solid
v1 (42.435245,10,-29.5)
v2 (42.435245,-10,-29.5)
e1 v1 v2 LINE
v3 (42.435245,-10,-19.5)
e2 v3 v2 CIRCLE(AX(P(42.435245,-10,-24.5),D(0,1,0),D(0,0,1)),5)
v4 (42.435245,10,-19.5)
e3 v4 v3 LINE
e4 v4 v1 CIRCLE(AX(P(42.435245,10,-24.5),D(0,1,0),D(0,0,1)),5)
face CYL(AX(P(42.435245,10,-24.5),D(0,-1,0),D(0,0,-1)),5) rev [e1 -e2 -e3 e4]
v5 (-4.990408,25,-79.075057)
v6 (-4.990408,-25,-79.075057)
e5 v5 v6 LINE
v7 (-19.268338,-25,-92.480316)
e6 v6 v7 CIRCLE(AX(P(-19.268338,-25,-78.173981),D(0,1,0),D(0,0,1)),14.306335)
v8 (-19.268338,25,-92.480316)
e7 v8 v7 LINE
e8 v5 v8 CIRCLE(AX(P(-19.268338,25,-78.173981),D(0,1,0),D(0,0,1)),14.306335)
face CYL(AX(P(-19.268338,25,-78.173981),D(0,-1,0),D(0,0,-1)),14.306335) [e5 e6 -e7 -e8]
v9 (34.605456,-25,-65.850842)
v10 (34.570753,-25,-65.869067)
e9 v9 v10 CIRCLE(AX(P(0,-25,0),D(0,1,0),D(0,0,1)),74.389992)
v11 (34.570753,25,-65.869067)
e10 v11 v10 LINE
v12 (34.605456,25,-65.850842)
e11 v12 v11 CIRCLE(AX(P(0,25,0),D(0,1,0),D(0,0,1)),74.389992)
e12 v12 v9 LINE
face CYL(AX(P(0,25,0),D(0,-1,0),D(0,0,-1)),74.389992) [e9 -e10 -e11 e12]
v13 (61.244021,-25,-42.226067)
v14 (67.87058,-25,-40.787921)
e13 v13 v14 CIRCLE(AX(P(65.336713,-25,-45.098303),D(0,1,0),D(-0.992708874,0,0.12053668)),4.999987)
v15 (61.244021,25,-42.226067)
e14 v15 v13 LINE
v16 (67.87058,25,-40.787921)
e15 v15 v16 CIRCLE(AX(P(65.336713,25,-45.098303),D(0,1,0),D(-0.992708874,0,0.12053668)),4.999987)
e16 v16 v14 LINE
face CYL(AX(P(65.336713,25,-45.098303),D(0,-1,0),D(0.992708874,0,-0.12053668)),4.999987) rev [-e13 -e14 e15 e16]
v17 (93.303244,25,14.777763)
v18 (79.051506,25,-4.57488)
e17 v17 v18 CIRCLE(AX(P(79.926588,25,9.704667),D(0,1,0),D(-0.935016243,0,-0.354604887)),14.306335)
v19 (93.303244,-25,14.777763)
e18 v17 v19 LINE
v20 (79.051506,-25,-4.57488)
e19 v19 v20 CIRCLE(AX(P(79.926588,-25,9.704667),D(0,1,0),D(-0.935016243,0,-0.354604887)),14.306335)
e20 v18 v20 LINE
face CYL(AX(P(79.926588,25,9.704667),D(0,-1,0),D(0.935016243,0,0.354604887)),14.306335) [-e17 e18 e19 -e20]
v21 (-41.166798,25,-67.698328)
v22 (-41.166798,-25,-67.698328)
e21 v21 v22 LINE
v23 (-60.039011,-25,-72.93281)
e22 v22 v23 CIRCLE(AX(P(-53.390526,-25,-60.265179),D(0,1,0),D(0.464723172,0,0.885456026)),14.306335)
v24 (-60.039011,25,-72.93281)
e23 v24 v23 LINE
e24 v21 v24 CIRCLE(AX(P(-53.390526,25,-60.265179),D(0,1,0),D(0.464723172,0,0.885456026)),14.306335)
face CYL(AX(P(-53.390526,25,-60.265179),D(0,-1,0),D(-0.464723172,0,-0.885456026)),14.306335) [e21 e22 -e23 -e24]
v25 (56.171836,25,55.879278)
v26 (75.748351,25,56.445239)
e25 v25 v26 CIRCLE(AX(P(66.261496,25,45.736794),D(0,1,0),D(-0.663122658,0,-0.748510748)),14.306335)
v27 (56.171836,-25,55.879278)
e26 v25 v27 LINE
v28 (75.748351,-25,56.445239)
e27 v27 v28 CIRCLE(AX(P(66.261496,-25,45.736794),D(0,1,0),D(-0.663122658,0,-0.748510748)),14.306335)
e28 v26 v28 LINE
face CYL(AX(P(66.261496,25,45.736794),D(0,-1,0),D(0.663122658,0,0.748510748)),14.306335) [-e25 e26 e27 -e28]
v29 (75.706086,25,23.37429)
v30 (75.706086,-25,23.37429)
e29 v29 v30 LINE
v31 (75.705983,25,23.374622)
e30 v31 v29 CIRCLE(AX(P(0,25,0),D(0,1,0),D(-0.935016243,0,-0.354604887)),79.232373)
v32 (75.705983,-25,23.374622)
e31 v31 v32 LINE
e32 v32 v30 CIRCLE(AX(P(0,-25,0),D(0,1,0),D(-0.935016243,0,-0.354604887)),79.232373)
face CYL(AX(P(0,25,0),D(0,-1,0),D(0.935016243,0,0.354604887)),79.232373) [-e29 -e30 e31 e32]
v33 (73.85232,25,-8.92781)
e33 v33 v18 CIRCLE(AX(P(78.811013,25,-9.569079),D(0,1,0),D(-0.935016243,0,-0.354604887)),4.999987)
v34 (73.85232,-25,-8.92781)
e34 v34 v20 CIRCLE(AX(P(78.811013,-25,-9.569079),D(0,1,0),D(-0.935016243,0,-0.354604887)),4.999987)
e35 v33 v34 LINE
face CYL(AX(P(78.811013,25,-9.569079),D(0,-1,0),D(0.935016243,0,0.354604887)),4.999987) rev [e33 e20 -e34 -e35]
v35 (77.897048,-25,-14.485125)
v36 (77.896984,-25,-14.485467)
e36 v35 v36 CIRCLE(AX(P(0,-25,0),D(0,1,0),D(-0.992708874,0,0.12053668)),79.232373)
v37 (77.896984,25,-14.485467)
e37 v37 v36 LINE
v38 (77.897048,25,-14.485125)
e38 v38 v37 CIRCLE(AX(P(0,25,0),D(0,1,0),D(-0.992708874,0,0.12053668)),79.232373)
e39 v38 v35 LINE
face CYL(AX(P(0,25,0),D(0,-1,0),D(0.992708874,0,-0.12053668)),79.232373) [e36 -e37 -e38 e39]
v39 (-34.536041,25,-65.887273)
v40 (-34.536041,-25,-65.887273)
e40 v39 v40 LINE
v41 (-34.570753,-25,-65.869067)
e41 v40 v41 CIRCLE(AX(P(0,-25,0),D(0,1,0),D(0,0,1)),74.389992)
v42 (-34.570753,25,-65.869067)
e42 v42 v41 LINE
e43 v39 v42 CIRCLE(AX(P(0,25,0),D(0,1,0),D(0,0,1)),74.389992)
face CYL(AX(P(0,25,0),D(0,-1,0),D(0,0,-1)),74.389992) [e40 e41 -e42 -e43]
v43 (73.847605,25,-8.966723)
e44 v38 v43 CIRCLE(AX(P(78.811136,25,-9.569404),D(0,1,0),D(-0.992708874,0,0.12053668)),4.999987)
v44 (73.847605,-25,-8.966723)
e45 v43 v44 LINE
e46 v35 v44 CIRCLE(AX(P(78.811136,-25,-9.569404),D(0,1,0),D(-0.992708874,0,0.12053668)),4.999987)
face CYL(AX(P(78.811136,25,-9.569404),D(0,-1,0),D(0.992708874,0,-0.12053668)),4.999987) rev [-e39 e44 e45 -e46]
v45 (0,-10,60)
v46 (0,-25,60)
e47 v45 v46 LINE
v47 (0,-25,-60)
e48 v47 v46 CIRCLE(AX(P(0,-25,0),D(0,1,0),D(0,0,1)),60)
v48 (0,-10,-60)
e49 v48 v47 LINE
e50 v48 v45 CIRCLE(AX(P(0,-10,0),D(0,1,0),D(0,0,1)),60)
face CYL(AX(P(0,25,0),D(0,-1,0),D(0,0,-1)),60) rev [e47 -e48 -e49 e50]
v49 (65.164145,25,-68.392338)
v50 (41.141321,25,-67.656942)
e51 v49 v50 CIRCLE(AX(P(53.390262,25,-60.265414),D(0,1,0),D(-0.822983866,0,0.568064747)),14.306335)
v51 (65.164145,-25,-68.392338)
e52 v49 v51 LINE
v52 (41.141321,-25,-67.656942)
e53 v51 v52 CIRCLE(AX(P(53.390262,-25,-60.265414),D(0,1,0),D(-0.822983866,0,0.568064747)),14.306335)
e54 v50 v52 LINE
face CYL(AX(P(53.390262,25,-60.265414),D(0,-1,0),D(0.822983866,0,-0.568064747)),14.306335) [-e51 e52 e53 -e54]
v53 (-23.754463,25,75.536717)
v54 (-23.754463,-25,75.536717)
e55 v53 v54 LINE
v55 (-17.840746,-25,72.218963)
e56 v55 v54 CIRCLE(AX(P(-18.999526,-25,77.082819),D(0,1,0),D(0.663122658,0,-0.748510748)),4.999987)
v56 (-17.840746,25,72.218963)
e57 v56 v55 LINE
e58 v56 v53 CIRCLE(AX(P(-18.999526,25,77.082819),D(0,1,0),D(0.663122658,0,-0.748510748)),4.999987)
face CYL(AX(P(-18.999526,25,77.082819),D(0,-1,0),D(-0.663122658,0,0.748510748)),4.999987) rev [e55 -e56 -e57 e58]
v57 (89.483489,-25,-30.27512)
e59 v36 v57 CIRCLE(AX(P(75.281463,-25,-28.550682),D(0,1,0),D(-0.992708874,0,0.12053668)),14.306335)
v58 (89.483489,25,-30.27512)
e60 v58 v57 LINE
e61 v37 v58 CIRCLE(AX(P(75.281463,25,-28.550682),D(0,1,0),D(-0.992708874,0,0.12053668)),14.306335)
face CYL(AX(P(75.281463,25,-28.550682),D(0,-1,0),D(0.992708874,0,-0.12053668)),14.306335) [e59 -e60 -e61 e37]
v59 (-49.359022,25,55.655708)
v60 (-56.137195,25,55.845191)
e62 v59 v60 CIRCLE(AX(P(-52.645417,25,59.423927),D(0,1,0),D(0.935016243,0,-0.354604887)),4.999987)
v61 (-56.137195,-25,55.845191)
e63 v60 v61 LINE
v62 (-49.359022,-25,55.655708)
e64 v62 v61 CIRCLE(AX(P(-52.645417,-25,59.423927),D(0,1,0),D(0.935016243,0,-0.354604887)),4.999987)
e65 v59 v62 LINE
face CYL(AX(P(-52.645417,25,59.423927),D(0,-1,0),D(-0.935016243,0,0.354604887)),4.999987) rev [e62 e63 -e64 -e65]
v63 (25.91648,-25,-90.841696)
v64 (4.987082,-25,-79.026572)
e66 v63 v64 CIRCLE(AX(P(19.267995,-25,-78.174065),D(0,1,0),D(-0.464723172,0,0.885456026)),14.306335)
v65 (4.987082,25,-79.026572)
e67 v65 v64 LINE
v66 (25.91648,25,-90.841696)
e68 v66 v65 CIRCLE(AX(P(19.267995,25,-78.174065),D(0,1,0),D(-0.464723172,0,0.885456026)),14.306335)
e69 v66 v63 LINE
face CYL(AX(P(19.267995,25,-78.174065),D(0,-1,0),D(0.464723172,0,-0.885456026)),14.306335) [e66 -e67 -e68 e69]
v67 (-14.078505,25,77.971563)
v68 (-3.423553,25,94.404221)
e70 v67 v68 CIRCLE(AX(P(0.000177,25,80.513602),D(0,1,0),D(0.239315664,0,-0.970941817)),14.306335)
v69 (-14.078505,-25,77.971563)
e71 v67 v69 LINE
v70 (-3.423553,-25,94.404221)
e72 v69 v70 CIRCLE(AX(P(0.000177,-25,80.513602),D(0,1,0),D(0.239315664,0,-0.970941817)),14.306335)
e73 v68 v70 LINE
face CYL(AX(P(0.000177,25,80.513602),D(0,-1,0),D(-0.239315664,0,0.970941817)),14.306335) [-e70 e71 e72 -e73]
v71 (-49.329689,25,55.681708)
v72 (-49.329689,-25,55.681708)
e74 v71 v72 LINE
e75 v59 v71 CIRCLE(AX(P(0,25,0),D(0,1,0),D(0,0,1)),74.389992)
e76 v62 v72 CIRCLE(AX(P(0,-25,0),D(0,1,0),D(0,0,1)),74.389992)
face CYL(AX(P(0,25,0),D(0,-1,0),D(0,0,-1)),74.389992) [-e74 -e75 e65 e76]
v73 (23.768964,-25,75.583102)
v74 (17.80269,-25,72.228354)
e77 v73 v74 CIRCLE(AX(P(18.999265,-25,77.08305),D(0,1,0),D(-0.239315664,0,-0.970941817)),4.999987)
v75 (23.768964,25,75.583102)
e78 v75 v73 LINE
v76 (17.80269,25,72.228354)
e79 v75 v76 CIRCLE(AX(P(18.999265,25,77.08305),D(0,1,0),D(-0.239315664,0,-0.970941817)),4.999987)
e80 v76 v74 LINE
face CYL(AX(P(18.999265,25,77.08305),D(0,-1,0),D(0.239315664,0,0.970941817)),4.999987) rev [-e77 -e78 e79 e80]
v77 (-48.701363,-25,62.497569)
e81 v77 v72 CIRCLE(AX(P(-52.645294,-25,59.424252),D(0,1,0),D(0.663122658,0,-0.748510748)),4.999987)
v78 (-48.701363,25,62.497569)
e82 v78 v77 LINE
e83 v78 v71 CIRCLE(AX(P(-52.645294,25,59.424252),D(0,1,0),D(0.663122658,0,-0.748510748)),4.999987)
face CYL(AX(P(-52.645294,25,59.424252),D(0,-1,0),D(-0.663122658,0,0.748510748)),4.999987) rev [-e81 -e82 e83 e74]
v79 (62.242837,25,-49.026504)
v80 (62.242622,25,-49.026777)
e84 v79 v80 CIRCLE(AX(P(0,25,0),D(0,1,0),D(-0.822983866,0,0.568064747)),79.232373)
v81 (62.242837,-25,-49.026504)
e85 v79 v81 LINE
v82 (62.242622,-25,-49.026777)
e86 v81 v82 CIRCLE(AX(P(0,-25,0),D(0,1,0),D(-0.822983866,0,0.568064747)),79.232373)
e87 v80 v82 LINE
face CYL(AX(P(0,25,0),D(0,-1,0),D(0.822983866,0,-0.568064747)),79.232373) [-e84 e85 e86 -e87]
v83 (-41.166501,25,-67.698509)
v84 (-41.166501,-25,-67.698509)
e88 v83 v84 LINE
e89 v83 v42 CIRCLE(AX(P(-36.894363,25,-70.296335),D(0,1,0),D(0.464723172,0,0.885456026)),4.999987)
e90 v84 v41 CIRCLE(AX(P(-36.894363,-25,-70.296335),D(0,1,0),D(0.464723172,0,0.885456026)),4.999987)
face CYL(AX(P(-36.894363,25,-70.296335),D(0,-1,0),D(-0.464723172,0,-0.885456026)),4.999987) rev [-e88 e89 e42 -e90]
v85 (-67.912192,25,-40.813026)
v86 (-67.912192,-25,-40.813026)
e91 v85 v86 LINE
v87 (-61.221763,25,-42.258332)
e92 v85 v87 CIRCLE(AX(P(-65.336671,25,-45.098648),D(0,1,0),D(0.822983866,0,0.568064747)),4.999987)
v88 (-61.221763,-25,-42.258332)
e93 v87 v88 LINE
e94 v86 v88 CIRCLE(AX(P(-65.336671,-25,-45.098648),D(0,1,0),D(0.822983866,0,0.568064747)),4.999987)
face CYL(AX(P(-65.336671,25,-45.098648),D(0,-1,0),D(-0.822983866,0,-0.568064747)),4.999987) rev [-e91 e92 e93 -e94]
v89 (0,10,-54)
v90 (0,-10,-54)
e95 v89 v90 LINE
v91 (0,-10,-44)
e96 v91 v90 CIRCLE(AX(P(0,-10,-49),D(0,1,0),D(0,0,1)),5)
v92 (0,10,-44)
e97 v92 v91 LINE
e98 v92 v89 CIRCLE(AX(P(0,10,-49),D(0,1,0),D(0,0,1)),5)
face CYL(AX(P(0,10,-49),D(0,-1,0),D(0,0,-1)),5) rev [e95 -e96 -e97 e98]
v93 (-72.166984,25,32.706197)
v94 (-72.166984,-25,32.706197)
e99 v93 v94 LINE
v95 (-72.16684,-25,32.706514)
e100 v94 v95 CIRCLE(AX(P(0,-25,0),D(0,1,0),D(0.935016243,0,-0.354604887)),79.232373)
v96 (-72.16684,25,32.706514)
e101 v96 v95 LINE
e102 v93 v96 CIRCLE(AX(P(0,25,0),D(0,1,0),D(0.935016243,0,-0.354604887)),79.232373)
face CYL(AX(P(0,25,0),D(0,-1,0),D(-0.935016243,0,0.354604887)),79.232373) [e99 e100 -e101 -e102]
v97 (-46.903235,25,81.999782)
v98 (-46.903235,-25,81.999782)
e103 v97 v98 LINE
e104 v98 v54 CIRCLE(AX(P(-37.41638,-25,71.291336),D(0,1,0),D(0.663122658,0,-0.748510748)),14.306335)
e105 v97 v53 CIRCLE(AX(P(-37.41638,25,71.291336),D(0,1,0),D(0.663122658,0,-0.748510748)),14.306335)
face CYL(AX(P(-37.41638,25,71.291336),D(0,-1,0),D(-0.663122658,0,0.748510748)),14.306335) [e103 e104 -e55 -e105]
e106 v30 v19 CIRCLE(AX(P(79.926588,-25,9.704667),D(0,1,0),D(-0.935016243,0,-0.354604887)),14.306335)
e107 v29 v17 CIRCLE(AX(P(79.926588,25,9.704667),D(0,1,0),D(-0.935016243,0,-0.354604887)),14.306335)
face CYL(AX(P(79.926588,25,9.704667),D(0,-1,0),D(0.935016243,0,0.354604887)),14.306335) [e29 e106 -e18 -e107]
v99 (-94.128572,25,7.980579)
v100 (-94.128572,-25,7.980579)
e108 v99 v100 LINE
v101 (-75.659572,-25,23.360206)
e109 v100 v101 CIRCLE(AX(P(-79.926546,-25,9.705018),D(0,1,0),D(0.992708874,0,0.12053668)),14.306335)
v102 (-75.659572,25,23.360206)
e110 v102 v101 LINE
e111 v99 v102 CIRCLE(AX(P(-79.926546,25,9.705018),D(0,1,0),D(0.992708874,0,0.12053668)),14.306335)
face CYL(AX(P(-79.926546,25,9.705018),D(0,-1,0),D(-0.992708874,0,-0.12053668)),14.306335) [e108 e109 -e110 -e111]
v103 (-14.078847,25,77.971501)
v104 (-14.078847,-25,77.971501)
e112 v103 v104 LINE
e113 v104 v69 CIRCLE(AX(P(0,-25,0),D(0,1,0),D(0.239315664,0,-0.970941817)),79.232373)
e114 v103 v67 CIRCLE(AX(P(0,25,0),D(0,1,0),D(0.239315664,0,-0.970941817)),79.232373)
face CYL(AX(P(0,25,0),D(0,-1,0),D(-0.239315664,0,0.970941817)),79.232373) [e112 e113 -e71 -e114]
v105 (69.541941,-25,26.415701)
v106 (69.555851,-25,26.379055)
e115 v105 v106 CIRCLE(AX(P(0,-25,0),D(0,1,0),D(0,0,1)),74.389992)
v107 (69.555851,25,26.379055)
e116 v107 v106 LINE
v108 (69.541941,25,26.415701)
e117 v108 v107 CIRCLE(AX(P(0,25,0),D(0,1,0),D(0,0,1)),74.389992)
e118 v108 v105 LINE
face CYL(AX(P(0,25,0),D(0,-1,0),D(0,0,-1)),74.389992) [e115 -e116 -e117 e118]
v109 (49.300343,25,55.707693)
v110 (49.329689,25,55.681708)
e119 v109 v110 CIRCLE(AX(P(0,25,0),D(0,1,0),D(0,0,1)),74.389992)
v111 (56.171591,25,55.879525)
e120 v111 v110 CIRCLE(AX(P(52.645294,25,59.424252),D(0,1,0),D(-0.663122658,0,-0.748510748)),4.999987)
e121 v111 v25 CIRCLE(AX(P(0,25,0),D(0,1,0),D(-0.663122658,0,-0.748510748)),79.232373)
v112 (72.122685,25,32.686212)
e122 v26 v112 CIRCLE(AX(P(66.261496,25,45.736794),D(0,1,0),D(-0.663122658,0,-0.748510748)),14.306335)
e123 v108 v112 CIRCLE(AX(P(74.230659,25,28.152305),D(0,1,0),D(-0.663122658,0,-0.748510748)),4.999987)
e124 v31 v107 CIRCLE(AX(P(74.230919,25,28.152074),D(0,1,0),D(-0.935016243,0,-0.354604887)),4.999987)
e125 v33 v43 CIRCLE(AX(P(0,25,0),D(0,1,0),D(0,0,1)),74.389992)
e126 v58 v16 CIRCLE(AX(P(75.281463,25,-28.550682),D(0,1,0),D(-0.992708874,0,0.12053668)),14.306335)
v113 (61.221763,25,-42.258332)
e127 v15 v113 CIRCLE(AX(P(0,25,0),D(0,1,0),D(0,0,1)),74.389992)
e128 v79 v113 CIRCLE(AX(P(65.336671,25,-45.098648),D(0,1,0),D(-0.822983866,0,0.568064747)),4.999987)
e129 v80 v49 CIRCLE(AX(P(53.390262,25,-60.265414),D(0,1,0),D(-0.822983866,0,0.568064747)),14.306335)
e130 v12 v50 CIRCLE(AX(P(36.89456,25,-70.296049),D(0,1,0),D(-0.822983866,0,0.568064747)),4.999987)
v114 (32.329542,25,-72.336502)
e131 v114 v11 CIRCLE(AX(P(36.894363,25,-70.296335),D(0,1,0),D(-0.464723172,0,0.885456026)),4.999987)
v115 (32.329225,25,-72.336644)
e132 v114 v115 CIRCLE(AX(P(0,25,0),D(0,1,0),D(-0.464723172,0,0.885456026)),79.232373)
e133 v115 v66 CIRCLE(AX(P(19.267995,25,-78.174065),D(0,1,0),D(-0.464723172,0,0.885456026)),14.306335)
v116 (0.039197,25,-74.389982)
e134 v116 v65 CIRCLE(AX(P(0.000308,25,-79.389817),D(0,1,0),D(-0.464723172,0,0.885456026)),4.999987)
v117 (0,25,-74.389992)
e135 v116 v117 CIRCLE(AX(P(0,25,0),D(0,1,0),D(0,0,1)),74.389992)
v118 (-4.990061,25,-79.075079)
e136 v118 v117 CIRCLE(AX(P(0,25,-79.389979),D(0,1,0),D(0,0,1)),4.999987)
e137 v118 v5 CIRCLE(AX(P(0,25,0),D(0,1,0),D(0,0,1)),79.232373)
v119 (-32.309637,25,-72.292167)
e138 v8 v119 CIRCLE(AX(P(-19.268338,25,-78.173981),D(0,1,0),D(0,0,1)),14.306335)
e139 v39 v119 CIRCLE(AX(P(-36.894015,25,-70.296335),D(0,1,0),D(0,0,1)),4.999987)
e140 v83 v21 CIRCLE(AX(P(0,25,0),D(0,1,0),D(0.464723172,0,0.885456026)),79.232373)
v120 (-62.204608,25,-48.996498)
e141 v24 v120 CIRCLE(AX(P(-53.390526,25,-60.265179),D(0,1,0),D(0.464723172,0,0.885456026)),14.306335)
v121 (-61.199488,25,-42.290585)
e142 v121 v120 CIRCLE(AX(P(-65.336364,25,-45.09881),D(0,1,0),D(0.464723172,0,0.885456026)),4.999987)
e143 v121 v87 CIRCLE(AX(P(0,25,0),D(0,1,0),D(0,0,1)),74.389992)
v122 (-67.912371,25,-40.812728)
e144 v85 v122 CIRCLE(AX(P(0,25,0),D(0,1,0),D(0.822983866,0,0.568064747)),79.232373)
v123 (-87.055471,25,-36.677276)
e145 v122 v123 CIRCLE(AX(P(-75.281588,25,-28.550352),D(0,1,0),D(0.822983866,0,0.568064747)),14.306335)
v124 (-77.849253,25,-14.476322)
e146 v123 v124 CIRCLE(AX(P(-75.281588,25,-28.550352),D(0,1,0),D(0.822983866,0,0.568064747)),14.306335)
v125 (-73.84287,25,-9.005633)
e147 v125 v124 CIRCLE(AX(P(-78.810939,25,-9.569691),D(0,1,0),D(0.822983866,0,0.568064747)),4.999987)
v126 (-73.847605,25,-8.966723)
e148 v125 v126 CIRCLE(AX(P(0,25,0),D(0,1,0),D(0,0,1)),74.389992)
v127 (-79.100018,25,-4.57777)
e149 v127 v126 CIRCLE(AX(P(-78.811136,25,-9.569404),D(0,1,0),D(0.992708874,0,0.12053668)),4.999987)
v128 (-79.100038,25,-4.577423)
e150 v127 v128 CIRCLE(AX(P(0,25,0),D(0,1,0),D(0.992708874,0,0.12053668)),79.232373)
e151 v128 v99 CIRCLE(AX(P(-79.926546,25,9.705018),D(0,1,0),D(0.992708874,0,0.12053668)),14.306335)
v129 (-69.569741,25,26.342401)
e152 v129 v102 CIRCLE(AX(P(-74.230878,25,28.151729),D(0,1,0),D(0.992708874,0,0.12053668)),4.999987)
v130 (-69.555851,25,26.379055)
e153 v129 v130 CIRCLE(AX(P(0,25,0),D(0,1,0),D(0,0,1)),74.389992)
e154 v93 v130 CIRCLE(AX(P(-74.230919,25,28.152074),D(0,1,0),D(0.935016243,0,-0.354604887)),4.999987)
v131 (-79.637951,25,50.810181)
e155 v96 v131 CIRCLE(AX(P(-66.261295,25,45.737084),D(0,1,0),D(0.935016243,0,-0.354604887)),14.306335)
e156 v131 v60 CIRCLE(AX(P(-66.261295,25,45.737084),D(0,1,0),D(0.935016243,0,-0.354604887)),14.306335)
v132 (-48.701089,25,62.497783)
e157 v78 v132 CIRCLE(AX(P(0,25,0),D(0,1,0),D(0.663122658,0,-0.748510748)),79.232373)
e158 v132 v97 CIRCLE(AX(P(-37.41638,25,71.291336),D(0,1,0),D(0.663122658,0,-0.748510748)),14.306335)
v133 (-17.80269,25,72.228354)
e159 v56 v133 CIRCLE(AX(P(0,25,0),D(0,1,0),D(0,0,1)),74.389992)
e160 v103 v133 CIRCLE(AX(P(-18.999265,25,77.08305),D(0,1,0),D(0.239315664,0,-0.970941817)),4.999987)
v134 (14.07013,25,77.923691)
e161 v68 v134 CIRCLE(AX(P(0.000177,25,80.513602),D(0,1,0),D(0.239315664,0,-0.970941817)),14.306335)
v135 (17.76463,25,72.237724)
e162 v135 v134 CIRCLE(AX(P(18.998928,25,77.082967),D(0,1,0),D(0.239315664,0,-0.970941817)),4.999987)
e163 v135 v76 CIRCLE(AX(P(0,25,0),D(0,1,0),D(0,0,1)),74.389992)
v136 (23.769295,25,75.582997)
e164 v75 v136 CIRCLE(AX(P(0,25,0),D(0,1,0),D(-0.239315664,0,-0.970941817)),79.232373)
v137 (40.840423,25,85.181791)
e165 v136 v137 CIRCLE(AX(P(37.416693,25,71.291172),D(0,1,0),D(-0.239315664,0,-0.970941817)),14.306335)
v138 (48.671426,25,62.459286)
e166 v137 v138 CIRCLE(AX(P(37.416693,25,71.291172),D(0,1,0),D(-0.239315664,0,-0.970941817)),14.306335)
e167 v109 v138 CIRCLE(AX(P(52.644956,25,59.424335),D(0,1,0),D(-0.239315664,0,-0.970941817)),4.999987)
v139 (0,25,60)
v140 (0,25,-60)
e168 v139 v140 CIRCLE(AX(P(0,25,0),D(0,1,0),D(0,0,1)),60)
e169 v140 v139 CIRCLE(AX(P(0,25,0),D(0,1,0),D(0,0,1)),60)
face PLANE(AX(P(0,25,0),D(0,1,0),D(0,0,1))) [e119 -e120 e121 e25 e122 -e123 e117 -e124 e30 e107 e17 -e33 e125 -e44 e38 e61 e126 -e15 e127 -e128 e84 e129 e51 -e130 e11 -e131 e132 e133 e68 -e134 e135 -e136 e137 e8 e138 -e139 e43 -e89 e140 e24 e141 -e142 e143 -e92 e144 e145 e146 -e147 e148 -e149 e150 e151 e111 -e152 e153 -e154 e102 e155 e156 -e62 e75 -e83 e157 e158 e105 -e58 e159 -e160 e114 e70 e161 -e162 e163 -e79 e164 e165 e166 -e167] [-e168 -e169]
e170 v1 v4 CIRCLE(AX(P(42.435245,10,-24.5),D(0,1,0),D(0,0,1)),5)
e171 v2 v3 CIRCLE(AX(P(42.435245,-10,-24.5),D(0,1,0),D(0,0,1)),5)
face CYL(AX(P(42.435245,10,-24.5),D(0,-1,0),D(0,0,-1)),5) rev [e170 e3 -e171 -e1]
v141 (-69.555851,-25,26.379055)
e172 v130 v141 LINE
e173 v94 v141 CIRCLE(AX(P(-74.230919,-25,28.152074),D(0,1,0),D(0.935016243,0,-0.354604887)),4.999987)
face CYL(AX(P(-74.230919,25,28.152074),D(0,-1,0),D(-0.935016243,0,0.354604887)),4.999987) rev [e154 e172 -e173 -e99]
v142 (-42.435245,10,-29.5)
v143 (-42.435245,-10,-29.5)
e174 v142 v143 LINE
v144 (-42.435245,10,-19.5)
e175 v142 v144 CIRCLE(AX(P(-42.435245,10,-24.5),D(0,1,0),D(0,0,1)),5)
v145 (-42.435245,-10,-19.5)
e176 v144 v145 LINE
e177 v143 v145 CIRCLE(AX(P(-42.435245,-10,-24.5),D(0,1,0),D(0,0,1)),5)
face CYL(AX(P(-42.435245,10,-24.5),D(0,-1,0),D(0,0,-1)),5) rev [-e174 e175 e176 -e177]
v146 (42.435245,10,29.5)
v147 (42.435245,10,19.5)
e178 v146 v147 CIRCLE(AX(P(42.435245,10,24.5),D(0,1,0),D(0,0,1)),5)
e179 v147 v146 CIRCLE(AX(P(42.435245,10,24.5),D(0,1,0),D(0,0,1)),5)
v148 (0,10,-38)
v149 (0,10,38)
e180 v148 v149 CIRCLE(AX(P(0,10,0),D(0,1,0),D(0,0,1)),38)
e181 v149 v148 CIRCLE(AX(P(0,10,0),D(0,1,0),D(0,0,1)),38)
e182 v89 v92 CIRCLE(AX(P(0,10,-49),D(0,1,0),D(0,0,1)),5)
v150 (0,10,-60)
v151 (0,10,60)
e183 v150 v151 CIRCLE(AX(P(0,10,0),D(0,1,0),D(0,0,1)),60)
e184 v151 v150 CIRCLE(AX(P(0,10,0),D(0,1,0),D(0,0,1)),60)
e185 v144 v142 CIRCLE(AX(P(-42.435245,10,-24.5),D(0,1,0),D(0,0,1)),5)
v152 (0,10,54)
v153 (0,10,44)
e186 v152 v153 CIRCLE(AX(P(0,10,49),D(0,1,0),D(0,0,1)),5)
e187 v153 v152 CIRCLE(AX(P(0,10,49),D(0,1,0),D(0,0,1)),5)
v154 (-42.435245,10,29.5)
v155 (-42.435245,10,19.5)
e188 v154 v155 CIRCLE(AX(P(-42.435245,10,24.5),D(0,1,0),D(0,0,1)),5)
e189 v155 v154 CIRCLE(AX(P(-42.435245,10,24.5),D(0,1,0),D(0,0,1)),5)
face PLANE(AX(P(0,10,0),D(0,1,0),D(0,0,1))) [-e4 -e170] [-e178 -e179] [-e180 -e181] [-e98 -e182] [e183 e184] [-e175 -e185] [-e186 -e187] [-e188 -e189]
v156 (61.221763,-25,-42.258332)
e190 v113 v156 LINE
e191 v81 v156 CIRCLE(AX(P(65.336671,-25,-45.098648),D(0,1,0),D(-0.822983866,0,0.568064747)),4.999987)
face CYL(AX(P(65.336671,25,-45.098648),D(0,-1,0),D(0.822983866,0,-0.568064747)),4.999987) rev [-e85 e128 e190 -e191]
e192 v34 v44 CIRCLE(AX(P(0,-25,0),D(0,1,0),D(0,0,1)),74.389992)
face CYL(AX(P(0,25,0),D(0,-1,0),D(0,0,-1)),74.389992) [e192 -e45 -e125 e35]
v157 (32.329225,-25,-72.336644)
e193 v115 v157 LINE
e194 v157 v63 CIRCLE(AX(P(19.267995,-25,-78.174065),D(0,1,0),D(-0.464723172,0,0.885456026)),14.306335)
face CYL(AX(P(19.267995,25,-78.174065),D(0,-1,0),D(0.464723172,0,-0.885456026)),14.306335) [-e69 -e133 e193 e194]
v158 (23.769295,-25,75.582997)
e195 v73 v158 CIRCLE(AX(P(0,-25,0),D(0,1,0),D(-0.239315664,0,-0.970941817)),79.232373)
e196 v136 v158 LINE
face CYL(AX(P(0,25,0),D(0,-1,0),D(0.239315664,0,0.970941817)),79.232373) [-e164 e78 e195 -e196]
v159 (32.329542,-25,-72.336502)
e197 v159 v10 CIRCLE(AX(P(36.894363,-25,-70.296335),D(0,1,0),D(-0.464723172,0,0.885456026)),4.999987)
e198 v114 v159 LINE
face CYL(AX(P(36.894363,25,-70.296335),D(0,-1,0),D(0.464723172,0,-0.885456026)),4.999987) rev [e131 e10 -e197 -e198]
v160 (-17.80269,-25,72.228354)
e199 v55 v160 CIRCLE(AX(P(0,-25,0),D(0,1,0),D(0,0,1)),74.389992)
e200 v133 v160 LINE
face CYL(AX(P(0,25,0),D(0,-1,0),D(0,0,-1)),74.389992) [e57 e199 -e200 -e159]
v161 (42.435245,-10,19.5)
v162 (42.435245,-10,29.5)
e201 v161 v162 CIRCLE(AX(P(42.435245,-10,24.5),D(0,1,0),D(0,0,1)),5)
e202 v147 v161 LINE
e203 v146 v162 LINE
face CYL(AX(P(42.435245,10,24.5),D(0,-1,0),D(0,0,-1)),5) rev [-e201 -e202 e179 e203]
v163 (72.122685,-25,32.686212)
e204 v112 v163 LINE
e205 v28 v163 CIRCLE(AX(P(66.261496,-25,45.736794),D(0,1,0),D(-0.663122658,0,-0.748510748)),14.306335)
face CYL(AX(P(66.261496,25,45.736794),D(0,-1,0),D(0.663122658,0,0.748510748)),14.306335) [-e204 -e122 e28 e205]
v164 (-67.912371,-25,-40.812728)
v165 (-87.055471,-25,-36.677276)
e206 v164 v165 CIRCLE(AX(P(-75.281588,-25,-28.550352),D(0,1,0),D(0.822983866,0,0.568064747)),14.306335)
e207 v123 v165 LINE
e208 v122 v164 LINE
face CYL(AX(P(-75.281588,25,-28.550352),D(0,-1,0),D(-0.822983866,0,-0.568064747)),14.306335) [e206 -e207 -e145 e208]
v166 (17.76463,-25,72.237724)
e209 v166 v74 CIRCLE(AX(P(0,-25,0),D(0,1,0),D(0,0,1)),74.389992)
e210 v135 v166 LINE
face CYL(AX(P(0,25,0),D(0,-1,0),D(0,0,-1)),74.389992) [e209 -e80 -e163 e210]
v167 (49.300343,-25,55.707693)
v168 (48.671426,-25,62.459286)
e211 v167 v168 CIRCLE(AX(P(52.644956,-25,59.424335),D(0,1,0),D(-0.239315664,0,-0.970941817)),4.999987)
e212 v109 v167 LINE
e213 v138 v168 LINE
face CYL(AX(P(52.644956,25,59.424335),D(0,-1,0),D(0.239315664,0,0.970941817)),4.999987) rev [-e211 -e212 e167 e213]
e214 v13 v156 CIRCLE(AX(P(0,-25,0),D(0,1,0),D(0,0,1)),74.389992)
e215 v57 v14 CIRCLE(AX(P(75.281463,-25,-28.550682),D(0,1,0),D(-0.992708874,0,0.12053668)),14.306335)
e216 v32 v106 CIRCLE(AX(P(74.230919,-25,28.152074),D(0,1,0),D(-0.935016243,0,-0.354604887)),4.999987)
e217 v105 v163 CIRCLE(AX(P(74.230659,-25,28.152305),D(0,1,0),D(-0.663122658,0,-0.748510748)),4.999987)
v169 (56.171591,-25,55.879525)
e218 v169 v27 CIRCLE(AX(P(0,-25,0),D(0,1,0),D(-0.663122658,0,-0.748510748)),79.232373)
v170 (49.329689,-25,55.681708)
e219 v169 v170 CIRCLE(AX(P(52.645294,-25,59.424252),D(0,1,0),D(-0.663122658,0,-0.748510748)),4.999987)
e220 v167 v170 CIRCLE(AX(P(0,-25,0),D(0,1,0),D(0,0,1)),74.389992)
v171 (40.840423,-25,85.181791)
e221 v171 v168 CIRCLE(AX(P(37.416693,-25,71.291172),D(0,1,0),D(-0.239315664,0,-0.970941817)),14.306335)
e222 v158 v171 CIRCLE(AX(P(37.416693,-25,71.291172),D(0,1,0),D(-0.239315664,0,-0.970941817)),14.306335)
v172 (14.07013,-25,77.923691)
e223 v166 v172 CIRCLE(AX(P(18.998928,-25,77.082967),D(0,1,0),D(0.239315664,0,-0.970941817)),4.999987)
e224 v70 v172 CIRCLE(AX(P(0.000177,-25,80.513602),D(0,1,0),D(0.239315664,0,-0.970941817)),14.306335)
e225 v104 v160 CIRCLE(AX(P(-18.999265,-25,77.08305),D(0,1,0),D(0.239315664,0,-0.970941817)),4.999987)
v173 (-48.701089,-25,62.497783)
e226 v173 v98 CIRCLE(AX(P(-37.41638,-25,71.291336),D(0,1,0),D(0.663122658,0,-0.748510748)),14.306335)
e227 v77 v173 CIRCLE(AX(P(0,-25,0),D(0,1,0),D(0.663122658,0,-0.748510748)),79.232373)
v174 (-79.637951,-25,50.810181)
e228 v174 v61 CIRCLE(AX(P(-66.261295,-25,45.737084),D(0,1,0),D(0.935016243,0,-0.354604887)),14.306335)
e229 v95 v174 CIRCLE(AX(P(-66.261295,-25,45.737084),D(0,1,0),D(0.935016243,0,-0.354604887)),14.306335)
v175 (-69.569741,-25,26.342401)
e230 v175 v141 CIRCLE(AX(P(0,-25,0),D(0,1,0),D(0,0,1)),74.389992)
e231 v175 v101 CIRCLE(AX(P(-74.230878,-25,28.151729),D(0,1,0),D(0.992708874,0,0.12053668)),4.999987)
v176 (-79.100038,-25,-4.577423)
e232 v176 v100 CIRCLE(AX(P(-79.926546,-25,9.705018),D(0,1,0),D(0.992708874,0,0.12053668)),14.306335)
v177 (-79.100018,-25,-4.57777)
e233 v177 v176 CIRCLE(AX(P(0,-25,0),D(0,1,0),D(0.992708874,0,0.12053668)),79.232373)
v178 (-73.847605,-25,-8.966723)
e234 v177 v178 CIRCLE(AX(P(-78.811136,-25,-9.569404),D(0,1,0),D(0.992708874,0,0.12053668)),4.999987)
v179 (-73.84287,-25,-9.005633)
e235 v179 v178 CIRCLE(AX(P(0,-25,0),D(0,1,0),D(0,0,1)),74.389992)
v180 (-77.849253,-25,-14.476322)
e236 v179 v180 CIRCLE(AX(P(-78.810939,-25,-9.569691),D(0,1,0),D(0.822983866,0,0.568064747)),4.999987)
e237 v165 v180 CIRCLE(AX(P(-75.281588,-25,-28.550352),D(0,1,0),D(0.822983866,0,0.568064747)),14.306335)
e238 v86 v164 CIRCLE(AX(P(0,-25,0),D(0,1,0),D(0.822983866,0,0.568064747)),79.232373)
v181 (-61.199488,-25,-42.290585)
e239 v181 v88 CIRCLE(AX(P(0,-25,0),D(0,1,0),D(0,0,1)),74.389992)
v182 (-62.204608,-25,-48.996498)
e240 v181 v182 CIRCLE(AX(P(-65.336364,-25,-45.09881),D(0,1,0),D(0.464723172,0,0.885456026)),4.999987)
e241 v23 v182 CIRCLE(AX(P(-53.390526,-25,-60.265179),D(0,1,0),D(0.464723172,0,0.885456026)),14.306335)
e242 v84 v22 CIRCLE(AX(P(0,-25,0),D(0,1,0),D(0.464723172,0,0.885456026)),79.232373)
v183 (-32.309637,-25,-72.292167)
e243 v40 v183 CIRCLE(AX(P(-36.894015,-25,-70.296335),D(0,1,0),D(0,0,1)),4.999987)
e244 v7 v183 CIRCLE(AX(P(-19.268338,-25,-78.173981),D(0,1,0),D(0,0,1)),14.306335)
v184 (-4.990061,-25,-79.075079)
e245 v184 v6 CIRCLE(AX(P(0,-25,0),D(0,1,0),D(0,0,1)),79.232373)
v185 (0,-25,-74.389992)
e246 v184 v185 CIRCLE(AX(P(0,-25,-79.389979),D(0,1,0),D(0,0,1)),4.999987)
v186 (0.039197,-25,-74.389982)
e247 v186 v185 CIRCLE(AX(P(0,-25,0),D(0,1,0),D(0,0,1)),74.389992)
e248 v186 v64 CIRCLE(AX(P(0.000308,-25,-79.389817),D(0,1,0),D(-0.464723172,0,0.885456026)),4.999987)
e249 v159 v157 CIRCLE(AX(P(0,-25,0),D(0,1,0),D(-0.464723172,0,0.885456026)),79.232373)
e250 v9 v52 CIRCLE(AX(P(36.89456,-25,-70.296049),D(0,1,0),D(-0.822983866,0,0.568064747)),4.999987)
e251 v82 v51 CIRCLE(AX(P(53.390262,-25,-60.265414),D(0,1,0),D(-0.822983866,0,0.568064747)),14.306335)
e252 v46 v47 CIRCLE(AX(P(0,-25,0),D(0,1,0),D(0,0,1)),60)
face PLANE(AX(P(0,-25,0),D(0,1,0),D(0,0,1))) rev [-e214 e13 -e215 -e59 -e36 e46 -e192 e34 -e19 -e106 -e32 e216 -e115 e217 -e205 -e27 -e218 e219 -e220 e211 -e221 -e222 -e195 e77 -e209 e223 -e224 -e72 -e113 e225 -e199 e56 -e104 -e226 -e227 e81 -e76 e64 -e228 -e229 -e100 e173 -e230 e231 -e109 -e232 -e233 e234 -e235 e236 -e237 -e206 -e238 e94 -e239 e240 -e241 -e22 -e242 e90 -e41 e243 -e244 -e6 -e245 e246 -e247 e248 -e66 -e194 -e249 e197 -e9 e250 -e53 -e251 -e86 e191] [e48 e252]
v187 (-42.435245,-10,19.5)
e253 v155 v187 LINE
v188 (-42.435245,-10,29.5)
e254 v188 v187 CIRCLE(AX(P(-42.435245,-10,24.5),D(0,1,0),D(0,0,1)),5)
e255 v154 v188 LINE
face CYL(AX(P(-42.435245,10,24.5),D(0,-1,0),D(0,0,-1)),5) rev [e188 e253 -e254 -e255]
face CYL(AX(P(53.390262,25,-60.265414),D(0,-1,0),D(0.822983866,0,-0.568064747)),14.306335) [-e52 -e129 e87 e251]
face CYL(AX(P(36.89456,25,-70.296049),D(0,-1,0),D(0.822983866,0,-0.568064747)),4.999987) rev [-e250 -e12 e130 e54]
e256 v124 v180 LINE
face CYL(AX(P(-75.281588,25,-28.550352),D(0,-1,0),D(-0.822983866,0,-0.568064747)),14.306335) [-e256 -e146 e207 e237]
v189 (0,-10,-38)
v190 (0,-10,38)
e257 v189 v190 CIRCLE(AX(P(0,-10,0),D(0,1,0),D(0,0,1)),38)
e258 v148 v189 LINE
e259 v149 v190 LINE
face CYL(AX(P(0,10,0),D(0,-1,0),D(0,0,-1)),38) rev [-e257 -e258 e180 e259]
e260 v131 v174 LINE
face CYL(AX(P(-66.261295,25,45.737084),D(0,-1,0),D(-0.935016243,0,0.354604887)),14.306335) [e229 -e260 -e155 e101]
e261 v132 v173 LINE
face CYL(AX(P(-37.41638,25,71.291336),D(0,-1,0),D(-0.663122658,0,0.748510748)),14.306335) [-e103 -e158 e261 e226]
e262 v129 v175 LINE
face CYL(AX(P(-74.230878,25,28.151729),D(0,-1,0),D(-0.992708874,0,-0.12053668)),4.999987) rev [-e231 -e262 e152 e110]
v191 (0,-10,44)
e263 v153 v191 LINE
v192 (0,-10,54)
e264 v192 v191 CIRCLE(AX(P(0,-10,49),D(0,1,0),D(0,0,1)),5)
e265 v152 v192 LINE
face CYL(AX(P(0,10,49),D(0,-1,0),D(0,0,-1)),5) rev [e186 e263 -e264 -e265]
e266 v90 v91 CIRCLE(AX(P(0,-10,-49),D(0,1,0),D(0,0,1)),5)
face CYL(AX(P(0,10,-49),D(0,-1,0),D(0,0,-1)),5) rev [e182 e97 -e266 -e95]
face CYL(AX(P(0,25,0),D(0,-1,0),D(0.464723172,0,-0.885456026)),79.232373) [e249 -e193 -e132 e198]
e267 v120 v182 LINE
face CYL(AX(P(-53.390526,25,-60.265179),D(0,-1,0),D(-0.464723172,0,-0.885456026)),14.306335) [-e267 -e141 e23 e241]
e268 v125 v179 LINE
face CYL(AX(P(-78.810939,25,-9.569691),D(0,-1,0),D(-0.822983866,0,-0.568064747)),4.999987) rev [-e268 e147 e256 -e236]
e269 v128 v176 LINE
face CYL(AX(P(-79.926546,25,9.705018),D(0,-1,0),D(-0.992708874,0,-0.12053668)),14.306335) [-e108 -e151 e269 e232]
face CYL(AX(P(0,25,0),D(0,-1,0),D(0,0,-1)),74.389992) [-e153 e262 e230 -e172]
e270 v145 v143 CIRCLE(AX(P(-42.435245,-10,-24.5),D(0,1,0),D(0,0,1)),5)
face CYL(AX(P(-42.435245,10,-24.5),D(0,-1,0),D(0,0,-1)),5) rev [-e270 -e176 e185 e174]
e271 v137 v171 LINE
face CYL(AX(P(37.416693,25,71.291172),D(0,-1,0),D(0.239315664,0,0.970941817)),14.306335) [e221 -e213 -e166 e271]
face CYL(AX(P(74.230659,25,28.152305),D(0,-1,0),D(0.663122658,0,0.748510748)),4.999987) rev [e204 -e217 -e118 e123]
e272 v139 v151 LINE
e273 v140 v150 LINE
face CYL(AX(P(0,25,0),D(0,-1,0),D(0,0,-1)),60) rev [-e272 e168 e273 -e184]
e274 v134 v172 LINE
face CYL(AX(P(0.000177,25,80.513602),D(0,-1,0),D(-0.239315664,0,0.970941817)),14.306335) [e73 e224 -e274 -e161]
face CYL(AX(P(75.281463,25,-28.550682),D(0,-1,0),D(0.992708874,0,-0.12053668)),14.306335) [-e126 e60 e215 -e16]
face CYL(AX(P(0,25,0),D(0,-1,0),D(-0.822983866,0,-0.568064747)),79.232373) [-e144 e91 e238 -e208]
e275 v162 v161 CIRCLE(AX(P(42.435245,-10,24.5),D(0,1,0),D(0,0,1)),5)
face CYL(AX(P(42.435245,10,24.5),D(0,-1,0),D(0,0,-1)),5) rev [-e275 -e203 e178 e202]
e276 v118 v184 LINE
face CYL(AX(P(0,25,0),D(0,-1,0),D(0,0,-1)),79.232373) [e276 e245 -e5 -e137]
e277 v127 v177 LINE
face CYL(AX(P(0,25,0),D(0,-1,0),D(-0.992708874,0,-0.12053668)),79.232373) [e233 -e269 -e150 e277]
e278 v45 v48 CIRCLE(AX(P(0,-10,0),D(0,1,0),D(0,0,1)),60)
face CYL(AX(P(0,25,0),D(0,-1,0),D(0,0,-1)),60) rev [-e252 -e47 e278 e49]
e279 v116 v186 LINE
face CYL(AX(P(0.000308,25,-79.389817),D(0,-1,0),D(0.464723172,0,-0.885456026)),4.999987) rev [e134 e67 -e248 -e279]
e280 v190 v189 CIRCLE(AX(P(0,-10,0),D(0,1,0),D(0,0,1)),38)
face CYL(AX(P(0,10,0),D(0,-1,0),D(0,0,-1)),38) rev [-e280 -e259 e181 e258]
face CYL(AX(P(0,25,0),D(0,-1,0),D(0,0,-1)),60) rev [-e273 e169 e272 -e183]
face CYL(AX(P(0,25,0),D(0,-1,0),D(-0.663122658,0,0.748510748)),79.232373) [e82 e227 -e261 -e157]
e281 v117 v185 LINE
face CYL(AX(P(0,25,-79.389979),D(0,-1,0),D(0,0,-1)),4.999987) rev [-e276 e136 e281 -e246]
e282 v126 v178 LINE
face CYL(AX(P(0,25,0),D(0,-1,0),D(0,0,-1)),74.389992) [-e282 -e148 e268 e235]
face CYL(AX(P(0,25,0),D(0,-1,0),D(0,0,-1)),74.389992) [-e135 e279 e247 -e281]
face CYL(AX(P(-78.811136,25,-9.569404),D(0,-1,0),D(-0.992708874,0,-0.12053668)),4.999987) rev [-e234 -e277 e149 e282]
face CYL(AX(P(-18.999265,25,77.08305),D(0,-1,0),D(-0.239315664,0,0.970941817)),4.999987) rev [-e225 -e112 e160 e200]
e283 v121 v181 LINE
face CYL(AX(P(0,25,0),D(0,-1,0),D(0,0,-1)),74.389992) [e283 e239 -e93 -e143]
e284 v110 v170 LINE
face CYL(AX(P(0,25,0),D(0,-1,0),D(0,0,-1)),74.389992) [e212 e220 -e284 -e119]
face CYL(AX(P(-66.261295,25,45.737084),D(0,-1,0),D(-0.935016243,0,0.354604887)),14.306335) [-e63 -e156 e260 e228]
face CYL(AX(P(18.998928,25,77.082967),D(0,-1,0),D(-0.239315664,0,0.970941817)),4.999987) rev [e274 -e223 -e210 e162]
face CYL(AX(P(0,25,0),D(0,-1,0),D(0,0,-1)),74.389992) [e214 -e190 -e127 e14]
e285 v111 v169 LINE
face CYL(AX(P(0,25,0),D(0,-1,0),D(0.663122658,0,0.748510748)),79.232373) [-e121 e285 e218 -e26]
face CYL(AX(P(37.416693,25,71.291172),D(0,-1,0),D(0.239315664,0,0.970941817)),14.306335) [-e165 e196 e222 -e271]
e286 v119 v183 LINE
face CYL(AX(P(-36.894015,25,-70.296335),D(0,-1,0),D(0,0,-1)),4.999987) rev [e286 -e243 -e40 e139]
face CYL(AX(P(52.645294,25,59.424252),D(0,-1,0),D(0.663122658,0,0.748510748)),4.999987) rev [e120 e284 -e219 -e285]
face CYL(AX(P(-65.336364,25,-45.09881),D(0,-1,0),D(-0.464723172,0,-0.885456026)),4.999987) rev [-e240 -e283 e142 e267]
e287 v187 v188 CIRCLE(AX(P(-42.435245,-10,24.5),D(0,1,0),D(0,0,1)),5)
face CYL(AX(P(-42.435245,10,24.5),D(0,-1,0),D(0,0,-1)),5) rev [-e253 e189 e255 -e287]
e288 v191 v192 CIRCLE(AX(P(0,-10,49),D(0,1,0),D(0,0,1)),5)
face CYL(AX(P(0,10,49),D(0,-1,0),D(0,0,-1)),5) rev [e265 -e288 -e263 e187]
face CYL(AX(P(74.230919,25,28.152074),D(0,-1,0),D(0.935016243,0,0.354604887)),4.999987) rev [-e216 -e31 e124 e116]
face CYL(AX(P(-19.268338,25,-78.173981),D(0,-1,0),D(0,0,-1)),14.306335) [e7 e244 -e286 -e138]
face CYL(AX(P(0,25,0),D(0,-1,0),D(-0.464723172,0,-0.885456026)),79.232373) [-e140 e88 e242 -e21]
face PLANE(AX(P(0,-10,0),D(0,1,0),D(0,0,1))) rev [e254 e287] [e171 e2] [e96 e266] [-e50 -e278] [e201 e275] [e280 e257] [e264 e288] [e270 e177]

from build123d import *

# Parameters (mm, degrees)
EXTRUDE_1_DEPTH          = 25
SKETCH_3_R               = 74.389991886
SKETCH_3_R_2             = 60
EXTRUDE_2_DEPTH          = 25
PATTERN_CIRCULAR_1_COUNT = 13
SKETCH_4_R               = 60
SKETCH_4_R_2             = 38
SKETCH_4_R_3             = 5
EXTRUDE_3_DEPTH          = 10


with BuildPart() as part:
    # 草图2 → 凸台-拉伸1 (new, symmetric)
    with BuildSketch(Plane(origin=(0, 0, 0), x_dir=(1, 0, 0), z_dir=(0, 1, 0))):
        with BuildLine():
            ThreePointArc((-34.536040721, 65.887273309), (-17.783660561, 72.233041676), (0, 74.389991886))
            ThreePointArc((0, 74.389991886), (-3.422380364, 75.744820223), (-4.990060614, 79.075079343))
            ThreePointArc((-4.990060614, 79.075079343), (-4.990234092, 79.075068396), (-4.990407571, 79.075057448))
            ThreePointArc((-4.990407571, 79.075057448), (-22.715686348, 92.058757055), (-32.30963725, 72.292167331))
            ThreePointArc((-32.30963725, 72.292167331), (-32.171226647, 68.654647695), (-34.536040721, 65.887273309))
        make_face()
    extrude_1 = extrude(amount=EXTRUDE_1_DEPTH, both=True)

    # 草图3 → 凸台-拉伸2 (add, symmetric)
    with BuildSketch(Plane(origin=(0, 0, 0), x_dir=(1, 0, 0), z_dir=(0, 1, 0))):
        Circle(SKETCH_3_R)
        with Locations(Location((0, 0, 0), (0, 0, 270))):
            Circle(SKETCH_3_R_2, mode=Mode.SUBTRACT)
    extrude(amount=EXTRUDE_2_DEPTH, both=True)

    # 阵列(圆周)1: 凸台-拉伸1 ×13 about axis
    pattern_circular_1_axis = Axis((0, 0, 0), (0, 1, 0))
    for i in range(1, PATTERN_CIRCULAR_1_COUNT):
        add(extrude_1.rotate(pattern_circular_1_axis, i * 360 / PATTERN_CIRCULAR_1_COUNT))

    # 草图4 → 凸台-拉伸3 (add, symmetric)
    with BuildSketch(Plane(origin=(0, 0, 0), x_dir=(1, 0, 0), z_dir=(0, 1, 0))):
        with Locations(Location((0, 0, 0), (0, 0, 270))):
            Circle(SKETCH_4_R)
        with Locations(Location((0, 0, 0), (0, 0, 270))):
            Circle(SKETCH_4_R_2, mode=Mode.SUBTRACT)
        with Locations(Location((0, 49, 0), (0, 0, 270))):
            Circle(SKETCH_4_R_3, mode=Mode.SUBTRACT)
        with Locations(Location((42.435244785, 24.5, 0), (0, 0, 270))):
            Circle(SKETCH_4_R_3, mode=Mode.SUBTRACT)
        with Locations(Location((42.435244785, -24.5, 0), (0, 0, 270))):
            Circle(SKETCH_4_R_3, mode=Mode.SUBTRACT)
        with Locations(Location((0, -49, 0), (0, 0, 270))):
            Circle(SKETCH_4_R_3, mode=Mode.SUBTRACT)
        with Locations(Location((-42.435244785, -24.5, 0), (0, 0, 270))):
            Circle(SKETCH_4_R_3, mode=Mode.SUBTRACT)
        with Locations(Location((-42.435244785, 24.5, 0), (0, 0, 270))):
            Circle(SKETCH_4_R_3, mode=Mode.SUBTRACT)
    extrude(amount=EXTRUDE_3_DEPTH, both=True)


solid = part.part
